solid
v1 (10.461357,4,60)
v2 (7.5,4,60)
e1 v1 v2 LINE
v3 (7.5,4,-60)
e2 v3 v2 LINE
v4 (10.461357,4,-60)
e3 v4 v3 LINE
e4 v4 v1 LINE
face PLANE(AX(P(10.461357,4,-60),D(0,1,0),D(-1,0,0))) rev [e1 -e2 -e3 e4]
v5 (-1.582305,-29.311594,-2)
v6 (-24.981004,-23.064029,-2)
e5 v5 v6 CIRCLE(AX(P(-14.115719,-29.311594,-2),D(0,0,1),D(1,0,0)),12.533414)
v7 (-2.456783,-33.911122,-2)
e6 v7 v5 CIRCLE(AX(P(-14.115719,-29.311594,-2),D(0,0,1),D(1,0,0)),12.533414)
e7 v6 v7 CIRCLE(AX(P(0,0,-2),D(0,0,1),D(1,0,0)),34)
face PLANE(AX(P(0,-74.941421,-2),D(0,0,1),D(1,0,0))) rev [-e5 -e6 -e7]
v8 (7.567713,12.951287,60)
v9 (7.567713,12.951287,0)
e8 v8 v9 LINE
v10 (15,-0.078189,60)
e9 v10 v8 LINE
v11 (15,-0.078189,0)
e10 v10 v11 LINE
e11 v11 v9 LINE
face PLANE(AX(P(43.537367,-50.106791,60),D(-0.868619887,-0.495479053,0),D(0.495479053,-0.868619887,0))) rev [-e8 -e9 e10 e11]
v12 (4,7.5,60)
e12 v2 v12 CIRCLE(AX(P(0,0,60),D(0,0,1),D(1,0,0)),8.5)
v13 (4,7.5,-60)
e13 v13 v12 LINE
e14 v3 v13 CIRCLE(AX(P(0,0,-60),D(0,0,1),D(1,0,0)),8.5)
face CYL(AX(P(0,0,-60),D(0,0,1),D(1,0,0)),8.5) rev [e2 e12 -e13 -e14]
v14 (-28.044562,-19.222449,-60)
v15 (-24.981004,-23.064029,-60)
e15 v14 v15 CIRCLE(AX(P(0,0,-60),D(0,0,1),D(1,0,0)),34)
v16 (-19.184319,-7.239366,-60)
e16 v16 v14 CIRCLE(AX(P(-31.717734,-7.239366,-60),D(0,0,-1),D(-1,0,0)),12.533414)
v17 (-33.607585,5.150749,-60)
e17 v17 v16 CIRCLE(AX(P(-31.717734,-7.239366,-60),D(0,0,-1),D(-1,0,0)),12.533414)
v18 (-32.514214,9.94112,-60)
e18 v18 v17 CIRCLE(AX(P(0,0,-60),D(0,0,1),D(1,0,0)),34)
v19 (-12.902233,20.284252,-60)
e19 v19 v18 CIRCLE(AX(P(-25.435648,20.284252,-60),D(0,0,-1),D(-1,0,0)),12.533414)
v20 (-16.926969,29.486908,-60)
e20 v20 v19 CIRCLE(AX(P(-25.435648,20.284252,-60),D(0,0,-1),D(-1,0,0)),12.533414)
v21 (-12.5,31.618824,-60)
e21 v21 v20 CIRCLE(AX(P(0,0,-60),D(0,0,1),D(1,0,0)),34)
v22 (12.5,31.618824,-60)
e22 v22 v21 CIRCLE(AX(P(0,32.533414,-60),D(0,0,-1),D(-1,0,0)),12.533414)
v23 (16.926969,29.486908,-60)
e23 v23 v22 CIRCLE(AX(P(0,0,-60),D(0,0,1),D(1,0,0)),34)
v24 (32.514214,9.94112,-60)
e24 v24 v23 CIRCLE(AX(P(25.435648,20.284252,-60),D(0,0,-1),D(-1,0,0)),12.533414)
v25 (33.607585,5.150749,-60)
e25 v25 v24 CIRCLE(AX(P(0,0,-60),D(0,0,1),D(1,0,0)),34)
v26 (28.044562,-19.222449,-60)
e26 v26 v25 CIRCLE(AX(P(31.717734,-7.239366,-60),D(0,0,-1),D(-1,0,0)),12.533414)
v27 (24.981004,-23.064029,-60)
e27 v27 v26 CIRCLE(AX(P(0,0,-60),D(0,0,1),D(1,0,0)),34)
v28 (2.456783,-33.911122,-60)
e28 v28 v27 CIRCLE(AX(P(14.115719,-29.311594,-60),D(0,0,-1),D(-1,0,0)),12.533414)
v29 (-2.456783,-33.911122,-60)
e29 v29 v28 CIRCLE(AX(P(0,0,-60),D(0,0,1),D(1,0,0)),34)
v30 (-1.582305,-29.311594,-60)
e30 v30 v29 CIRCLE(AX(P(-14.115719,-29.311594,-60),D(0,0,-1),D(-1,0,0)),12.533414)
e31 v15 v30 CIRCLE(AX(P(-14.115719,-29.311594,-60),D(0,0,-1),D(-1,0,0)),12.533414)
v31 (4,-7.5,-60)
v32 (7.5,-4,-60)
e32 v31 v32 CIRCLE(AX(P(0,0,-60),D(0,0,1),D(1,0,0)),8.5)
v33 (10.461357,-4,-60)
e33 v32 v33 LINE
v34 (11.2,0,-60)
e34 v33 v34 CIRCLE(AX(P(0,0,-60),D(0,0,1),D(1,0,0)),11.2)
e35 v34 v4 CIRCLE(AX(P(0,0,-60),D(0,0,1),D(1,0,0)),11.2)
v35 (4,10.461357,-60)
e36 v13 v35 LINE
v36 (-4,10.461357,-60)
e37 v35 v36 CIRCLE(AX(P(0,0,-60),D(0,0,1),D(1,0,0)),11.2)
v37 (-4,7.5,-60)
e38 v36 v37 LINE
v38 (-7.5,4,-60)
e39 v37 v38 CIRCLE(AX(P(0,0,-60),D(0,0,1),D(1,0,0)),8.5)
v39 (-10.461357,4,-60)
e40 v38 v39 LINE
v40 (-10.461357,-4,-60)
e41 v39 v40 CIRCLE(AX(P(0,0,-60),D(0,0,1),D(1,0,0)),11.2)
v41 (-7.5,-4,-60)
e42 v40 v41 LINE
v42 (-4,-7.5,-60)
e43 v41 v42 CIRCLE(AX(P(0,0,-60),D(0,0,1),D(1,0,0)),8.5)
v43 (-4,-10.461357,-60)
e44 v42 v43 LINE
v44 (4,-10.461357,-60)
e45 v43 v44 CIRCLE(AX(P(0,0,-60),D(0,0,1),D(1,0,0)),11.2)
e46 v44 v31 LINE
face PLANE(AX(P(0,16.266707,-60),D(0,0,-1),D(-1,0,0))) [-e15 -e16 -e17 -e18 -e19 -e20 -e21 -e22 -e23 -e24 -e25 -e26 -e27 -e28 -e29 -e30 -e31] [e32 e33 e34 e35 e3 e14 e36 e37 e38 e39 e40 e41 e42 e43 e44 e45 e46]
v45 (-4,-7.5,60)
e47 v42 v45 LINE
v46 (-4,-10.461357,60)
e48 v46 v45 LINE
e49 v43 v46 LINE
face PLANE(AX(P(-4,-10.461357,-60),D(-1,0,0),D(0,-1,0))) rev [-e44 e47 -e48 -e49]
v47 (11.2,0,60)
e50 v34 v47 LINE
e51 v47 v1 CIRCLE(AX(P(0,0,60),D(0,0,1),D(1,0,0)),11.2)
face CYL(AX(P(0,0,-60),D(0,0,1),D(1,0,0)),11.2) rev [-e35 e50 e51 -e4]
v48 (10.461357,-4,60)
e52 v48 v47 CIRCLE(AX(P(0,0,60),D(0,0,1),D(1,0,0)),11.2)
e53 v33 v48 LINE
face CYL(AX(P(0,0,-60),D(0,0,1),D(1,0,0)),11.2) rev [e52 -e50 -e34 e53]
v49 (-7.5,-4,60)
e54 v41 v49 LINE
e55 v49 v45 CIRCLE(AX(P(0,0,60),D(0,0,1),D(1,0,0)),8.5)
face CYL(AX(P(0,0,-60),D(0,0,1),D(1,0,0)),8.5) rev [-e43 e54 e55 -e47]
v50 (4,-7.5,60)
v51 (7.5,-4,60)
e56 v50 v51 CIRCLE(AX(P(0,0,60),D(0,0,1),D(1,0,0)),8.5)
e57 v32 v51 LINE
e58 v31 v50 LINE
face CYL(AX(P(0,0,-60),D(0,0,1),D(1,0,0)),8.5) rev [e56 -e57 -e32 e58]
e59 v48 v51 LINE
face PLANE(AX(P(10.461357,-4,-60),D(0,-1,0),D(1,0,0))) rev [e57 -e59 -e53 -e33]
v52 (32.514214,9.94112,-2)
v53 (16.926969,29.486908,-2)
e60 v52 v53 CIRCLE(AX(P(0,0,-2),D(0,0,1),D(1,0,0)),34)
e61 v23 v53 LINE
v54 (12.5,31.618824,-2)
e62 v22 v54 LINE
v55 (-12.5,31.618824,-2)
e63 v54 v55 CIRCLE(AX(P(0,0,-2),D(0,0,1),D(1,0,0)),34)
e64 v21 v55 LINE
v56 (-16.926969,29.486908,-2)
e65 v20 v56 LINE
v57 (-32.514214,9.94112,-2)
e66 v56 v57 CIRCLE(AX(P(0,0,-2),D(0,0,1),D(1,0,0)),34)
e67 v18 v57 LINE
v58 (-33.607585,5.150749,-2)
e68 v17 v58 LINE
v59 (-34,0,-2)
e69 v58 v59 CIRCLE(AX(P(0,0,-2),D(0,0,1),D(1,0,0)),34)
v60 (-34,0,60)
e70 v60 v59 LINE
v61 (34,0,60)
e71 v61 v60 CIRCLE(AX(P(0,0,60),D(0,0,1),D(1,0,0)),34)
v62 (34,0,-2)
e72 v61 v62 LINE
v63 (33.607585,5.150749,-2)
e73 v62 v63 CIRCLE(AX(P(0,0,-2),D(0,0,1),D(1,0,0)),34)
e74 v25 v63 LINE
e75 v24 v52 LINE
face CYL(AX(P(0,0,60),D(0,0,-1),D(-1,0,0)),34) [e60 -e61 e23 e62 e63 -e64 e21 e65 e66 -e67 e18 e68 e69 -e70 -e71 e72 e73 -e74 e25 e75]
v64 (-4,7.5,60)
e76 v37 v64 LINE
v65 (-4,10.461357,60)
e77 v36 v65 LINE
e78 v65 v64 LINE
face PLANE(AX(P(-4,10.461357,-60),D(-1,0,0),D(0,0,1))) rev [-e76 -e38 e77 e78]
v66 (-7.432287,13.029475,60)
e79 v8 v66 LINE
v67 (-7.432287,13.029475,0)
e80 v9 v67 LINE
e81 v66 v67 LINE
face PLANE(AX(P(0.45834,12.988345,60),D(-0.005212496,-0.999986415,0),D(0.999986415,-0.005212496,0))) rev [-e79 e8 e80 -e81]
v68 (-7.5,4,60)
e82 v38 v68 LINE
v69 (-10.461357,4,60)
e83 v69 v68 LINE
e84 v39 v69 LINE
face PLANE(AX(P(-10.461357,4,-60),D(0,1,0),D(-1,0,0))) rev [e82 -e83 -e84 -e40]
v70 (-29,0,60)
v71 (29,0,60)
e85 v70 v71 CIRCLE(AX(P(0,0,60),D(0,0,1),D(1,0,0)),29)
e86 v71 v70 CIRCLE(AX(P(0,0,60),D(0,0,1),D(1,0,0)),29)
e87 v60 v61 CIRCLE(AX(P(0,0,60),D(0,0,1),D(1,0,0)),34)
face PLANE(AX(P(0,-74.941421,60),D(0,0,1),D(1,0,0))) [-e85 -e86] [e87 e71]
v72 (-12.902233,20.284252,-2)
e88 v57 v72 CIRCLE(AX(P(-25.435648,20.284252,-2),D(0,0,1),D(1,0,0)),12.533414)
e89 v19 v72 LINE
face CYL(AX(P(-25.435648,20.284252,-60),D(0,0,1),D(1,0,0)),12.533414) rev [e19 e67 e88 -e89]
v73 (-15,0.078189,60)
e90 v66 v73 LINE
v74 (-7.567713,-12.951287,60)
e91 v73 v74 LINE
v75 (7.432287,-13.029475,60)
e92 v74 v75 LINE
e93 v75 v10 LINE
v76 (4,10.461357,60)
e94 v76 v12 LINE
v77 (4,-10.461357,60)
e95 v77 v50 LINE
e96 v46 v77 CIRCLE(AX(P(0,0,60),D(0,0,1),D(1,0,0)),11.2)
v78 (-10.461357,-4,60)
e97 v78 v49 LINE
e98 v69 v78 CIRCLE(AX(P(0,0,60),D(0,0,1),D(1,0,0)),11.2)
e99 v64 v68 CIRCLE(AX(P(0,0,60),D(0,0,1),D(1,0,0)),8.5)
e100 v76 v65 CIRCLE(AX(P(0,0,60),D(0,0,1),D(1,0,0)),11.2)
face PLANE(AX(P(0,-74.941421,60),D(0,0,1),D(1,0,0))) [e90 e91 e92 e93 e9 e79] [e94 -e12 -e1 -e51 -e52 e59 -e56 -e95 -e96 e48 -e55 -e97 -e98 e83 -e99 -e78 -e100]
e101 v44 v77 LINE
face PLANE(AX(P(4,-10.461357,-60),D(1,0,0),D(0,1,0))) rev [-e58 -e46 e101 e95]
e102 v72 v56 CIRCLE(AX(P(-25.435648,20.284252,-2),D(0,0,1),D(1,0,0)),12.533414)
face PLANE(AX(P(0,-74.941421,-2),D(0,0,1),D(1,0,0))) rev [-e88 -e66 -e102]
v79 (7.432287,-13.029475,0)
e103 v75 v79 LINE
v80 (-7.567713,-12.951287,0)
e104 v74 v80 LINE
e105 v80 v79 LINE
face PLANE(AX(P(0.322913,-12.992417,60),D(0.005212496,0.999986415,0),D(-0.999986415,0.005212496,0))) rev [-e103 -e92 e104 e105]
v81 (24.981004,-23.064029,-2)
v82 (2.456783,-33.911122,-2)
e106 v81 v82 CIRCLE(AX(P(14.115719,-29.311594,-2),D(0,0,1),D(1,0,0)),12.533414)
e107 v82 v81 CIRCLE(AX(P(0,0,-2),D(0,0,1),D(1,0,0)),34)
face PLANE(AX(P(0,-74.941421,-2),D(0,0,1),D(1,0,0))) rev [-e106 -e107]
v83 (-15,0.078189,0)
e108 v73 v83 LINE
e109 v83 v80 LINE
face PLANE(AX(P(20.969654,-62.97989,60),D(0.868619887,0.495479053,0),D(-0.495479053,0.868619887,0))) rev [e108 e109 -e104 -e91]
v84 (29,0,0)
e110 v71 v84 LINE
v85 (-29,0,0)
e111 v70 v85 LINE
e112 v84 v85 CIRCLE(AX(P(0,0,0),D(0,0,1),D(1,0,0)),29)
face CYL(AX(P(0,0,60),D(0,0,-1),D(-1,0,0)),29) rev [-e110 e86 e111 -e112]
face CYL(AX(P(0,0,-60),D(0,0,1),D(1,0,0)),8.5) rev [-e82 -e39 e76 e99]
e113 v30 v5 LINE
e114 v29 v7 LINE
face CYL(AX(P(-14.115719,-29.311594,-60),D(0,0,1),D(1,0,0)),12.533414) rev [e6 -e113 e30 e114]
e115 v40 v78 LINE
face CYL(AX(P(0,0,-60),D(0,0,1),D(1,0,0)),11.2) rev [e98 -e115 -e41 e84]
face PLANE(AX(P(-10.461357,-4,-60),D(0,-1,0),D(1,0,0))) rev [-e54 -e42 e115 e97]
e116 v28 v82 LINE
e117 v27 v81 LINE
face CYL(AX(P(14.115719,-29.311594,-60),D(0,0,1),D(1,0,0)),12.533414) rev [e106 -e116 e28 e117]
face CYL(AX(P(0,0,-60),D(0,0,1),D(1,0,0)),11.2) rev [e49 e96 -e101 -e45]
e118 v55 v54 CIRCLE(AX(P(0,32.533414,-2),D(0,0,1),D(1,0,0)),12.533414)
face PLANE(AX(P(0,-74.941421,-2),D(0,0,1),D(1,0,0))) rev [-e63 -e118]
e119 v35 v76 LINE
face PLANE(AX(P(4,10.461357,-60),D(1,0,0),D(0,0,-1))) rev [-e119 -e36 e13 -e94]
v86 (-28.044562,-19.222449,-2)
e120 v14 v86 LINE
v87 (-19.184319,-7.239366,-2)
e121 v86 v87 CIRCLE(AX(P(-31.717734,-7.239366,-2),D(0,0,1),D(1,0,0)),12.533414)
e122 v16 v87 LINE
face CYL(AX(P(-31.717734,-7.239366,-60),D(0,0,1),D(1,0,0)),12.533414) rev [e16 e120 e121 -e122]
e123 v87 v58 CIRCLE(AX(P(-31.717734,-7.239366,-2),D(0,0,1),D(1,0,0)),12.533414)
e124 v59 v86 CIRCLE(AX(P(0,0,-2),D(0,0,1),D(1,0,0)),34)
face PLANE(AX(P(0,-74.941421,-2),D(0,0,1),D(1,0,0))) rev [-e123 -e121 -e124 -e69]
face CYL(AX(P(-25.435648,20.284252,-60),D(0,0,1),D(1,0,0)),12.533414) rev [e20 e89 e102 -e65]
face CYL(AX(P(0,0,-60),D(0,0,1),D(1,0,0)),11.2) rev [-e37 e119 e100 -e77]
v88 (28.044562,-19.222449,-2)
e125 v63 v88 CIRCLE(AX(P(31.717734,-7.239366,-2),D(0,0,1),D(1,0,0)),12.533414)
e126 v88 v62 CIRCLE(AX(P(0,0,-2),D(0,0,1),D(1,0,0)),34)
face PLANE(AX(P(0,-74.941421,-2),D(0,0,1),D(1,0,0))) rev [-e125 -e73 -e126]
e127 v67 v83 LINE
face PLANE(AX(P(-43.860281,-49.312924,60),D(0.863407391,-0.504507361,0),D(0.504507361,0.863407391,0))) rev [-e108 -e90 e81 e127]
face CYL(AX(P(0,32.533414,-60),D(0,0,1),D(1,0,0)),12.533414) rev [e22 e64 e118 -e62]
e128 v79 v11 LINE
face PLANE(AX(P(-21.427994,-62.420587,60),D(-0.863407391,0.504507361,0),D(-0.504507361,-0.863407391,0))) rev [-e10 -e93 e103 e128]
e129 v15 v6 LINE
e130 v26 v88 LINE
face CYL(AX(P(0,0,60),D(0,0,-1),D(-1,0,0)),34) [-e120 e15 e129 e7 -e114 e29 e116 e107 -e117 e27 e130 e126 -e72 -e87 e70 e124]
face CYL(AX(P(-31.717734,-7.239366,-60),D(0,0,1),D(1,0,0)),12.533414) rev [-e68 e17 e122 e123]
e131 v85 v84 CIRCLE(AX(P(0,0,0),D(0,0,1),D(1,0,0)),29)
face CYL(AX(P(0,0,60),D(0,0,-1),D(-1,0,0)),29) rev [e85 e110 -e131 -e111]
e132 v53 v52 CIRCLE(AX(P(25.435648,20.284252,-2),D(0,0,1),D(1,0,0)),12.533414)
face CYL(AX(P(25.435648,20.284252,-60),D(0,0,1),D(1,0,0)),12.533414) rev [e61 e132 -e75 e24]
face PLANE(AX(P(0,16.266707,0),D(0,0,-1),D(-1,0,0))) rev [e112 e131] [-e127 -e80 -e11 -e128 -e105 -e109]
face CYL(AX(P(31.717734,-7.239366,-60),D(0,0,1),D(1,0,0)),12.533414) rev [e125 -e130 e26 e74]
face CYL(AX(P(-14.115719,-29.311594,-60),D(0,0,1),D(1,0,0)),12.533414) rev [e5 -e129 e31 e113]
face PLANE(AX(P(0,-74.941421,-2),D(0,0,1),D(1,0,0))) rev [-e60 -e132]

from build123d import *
from build123d.topology import SkipClean

# Parameters (mm, degrees)
SKETCH_1_R        = 34
SKETCH_1_R_2      = 29
EXTRUDE_1_DEPTH   = 60
EXTRUDE_1_2_DEPTH = 60
EXTRUDE_START     = -60
EXTRUDE_2_DEPTH   = 60
EXTRUDE_START_2   = -2
SKETCH_4_R        = 34
EXTRUDE_3_DEPTH   = 2


with BuildPart() as part:
    # 草图1 → 凸台-拉伸1 (new body)
    with BuildSketch(Plane.XY):
        Circle(SKETCH_1_R)
        Circle(SKETCH_1_R_2, mode=Mode.SUBTRACT)
    extrude(amount=EXTRUDE_1_DEPTH)



with BuildPart() as body_2:
    # 草图1 → Extrude 1 2 (new body)
    with BuildSketch(Plane.XY):
        Polygon((-15, 0.078188502), (-7.567713229, -12.951286806), (7.432286771, -13.029475308), (15, -0.078188502), (7.567713229, 12.951286806), (-7.432286771, 13.029475308), align=None)
        with BuildLine():
            ThreePointArc((-10.461357464, 4), (-11.2, 0), (-10.461357464, -4))
            Line((-10.461357464, -4), (-7.5, -4))
            ThreePointArc((-7.5, -4), (-6.01040764, -6.01040764), (-4, -7.5))
            Line((-4, -7.5), (-4, -10.461357464))
            ThreePointArc((-4, -10.461357464), (0, -11.2), (4, -10.461357464))
            Line((4, -10.461357464), (4, -7.5))
            ThreePointArc((4, -7.5), (6.01040764, -6.01040764), (7.5, -4))
            Line((7.5, -4), (10.461357464, -4))
            ThreePointArc((10.461357464, -4), (11.2, 0), (10.461357464, 4))
            Line((10.461357464, 4), (7.5, 4))
            ThreePointArc((7.5, 4), (6.01040764, 6.01040764), (4, 7.5))
            Line((4, 7.5), (4, 10.461357464))
            ThreePointArc((4, 10.461357464), (0, 11.2), (-4, 10.461357464))
            Line((-4, 10.461357464), (-4, 7.5))
            ThreePointArc((-4, 7.5), (-6.01040764, 6.01040764), (-7.5, 4))
            Line((-7.5, 4), (-10.461357464, 4))
        make_face(mode=Mode.SUBTRACT)
    extrude(amount=EXTRUDE_1_2_DEPTH)


with BuildPart() as part_1:
    add(part.part)

    add(body_2.part)  # 凸台-拉伸2 merges body 2
    # 草图2 → 凸台-拉伸2 (add)
    with BuildSketch(Plane.XY.offset(EXTRUDE_START)):
        with BuildLine():
            ThreePointArc((16.926969134, 29.486907535), (14.75204713, 30.632941509), (12.5, 31.618823508))
            ThreePointArc((12.5, 31.618823508), (0, 20), (-12.5, 31.618823508))
            ThreePointArc((-12.5, 31.618823508), (-14.75204713, 30.632941509), (-16.926969134, 29.486907535))
            ThreePointArc((-16.926969134, 29.486907535), (-15.636629649, 12.469796037), (-32.51421418, 9.941120473))
            ThreePointArc((-32.51421418, 9.941120473), (-33.147549014, 7.565711755), (-33.607585262, 5.150748765))
            ThreePointArc((-33.607585262, 5.150748765), (-19.498558244, -4.450418679), (-28.044561913, -19.22244904))
            ThreePointArc((-28.044561913, -19.22244904), (-26.582270404, -21.198653263), (-24.981004219, -23.064028881))
            ThreePointArc((-24.981004219, -23.064028881), (-8.677674782, -18.019377358), (-2.456782521, -33.911122359))
            ThreePointArc((-2.456782521, -33.911122359), (0, -34), (2.456782521, -33.911122359))
            ThreePointArc((2.456782521, -33.911122359), (8.677674782, -18.019377358), (24.981004219, -23.064028881))
            ThreePointArc((24.981004219, -23.064028881), (26.582270404, -21.198653263), (28.044561913, -19.22244904))
            ThreePointArc((28.044561913, -19.22244904), (19.498558244, -4.450418679), (33.607585262, 5.150748765))
            ThreePointArc((33.607585262, 5.150748765), (33.147549014, 7.565711755), (32.51421418, 9.941120473))
            ThreePointArc((32.51421418, 9.941120473), (15.636629649, 12.469796037), (16.926969134, 29.486907535))
        make_face()
        with BuildLine():
            Line((-10.461357464, -4), (-7.5, -4))
            ThreePointArc((-7.5, -4), (-6.01040764, -6.01040764), (-4, -7.5))
            Line((-4, -7.5), (-4, -10.461357464))
            ThreePointArc((-4, -10.461357464), (0, -11.2), (4, -10.461357464))
            Line((4, -10.461357464), (4, -7.5))
            ThreePointArc((4, -7.5), (6.01040764, -6.01040764), (7.5, -4))
            Line((7.5, -4), (10.461357464, -4))
            ThreePointArc((10.461357464, -4), (11.2, 0), (10.461357464, 4))
            Line((10.461357464, 4), (7.5, 4))
            ThreePointArc((7.5, 4), (6.01040764, 6.01040764), (4, 7.5))
            Line((4, 7.5), (4, 10.461357464))
            ThreePointArc((4, 10.461357464), (0, 11.2), (-4, 10.461357464))
            Line((-4, 10.461357464), (-4, 7.5))
            ThreePointArc((-4, 7.5), (-6.01040764, 6.01040764), (-7.5, 4))
            Line((-7.5, 4), (-10.461357464, 4))
            ThreePointArc((-10.461357464, 4), (-11.2, 0), (-10.461357464, -4))
        make_face(mode=Mode.SUBTRACT)
    extrude(amount=EXTRUDE_2_DEPTH)

    # 草图4 → 凸台-拉伸3 (add)
    with SkipClean():  # the faces are left unmerged after this step: merging them gives an invalid solid
        with BuildSketch(Plane.XY.offset(EXTRUDE_START_2)):
            with Locations(Location((0, 0, 0), (0, 0, 171.286564556))):
                Circle(SKETCH_4_R)
            with BuildLine():
                ThreePointArc((21.649435664, -19.295127245), (22.673112992, -18.081204254), (23.628810764, -16.813069377))
                ThreePointArc((23.628810764, -16.813069377), (19.498558244, -4.450418679), (28.583740291, 4.895895317))
                ThreePointArc((28.583740291, 4.895895317), (28.272909453, 6.453107085), (27.877309497, 7.990970854))
                ThreePointArc((27.877309497, 7.990970854), (15.636629649, 12.469796037), (13.993905477, 25.400208848))
                ThreePointArc((13.993905477, 25.400208848), (12.582628434, 26.128097169), (11.133625585, 26.777647046))
                ThreePointArc((11.133625585, 26.777647046), (0, 20), (-11.133625585, 26.777647046))
                ThreePointArc((-11.133625585, 26.777647046), (-12.582628434, 26.128097169), (-13.993905477, 25.400208848))
                ThreePointArc((-13.993905477, 25.400208848), (-15.636629649, 12.469796037), (-27.877309497, 7.990970854))
                ThreePointArc((-27.877309497, 7.990970854), (-28.272909453, 6.453107085), (-28.583740291, 4.895895317))
                ThreePointArc((-28.583740291, 4.895895317), (-19.498558244, -4.450418679), (-23.628810764, -16.813069377))
                ThreePointArc((-23.628810764, -16.813069377), (-22.673112992, -18.081204254), (-21.649435664, -19.295127245))
                ThreePointArc((-21.649435664, -19.295127245), (-8.677674782, -18.019377358), (-1.587335586, -28.956525443))
                ThreePointArc((-1.587335586, -28.956525443), (0, -29), (1.587335586, -28.956525443))
                ThreePointArc((1.587335586, -28.956525443), (8.677674782, -18.019377358), (21.649435664, -19.295127245))
            make_face(mode=Mode.SUBTRACT)
        extrude(amount=EXTRUDE_3_DEPTH)


solid = part_1.part
